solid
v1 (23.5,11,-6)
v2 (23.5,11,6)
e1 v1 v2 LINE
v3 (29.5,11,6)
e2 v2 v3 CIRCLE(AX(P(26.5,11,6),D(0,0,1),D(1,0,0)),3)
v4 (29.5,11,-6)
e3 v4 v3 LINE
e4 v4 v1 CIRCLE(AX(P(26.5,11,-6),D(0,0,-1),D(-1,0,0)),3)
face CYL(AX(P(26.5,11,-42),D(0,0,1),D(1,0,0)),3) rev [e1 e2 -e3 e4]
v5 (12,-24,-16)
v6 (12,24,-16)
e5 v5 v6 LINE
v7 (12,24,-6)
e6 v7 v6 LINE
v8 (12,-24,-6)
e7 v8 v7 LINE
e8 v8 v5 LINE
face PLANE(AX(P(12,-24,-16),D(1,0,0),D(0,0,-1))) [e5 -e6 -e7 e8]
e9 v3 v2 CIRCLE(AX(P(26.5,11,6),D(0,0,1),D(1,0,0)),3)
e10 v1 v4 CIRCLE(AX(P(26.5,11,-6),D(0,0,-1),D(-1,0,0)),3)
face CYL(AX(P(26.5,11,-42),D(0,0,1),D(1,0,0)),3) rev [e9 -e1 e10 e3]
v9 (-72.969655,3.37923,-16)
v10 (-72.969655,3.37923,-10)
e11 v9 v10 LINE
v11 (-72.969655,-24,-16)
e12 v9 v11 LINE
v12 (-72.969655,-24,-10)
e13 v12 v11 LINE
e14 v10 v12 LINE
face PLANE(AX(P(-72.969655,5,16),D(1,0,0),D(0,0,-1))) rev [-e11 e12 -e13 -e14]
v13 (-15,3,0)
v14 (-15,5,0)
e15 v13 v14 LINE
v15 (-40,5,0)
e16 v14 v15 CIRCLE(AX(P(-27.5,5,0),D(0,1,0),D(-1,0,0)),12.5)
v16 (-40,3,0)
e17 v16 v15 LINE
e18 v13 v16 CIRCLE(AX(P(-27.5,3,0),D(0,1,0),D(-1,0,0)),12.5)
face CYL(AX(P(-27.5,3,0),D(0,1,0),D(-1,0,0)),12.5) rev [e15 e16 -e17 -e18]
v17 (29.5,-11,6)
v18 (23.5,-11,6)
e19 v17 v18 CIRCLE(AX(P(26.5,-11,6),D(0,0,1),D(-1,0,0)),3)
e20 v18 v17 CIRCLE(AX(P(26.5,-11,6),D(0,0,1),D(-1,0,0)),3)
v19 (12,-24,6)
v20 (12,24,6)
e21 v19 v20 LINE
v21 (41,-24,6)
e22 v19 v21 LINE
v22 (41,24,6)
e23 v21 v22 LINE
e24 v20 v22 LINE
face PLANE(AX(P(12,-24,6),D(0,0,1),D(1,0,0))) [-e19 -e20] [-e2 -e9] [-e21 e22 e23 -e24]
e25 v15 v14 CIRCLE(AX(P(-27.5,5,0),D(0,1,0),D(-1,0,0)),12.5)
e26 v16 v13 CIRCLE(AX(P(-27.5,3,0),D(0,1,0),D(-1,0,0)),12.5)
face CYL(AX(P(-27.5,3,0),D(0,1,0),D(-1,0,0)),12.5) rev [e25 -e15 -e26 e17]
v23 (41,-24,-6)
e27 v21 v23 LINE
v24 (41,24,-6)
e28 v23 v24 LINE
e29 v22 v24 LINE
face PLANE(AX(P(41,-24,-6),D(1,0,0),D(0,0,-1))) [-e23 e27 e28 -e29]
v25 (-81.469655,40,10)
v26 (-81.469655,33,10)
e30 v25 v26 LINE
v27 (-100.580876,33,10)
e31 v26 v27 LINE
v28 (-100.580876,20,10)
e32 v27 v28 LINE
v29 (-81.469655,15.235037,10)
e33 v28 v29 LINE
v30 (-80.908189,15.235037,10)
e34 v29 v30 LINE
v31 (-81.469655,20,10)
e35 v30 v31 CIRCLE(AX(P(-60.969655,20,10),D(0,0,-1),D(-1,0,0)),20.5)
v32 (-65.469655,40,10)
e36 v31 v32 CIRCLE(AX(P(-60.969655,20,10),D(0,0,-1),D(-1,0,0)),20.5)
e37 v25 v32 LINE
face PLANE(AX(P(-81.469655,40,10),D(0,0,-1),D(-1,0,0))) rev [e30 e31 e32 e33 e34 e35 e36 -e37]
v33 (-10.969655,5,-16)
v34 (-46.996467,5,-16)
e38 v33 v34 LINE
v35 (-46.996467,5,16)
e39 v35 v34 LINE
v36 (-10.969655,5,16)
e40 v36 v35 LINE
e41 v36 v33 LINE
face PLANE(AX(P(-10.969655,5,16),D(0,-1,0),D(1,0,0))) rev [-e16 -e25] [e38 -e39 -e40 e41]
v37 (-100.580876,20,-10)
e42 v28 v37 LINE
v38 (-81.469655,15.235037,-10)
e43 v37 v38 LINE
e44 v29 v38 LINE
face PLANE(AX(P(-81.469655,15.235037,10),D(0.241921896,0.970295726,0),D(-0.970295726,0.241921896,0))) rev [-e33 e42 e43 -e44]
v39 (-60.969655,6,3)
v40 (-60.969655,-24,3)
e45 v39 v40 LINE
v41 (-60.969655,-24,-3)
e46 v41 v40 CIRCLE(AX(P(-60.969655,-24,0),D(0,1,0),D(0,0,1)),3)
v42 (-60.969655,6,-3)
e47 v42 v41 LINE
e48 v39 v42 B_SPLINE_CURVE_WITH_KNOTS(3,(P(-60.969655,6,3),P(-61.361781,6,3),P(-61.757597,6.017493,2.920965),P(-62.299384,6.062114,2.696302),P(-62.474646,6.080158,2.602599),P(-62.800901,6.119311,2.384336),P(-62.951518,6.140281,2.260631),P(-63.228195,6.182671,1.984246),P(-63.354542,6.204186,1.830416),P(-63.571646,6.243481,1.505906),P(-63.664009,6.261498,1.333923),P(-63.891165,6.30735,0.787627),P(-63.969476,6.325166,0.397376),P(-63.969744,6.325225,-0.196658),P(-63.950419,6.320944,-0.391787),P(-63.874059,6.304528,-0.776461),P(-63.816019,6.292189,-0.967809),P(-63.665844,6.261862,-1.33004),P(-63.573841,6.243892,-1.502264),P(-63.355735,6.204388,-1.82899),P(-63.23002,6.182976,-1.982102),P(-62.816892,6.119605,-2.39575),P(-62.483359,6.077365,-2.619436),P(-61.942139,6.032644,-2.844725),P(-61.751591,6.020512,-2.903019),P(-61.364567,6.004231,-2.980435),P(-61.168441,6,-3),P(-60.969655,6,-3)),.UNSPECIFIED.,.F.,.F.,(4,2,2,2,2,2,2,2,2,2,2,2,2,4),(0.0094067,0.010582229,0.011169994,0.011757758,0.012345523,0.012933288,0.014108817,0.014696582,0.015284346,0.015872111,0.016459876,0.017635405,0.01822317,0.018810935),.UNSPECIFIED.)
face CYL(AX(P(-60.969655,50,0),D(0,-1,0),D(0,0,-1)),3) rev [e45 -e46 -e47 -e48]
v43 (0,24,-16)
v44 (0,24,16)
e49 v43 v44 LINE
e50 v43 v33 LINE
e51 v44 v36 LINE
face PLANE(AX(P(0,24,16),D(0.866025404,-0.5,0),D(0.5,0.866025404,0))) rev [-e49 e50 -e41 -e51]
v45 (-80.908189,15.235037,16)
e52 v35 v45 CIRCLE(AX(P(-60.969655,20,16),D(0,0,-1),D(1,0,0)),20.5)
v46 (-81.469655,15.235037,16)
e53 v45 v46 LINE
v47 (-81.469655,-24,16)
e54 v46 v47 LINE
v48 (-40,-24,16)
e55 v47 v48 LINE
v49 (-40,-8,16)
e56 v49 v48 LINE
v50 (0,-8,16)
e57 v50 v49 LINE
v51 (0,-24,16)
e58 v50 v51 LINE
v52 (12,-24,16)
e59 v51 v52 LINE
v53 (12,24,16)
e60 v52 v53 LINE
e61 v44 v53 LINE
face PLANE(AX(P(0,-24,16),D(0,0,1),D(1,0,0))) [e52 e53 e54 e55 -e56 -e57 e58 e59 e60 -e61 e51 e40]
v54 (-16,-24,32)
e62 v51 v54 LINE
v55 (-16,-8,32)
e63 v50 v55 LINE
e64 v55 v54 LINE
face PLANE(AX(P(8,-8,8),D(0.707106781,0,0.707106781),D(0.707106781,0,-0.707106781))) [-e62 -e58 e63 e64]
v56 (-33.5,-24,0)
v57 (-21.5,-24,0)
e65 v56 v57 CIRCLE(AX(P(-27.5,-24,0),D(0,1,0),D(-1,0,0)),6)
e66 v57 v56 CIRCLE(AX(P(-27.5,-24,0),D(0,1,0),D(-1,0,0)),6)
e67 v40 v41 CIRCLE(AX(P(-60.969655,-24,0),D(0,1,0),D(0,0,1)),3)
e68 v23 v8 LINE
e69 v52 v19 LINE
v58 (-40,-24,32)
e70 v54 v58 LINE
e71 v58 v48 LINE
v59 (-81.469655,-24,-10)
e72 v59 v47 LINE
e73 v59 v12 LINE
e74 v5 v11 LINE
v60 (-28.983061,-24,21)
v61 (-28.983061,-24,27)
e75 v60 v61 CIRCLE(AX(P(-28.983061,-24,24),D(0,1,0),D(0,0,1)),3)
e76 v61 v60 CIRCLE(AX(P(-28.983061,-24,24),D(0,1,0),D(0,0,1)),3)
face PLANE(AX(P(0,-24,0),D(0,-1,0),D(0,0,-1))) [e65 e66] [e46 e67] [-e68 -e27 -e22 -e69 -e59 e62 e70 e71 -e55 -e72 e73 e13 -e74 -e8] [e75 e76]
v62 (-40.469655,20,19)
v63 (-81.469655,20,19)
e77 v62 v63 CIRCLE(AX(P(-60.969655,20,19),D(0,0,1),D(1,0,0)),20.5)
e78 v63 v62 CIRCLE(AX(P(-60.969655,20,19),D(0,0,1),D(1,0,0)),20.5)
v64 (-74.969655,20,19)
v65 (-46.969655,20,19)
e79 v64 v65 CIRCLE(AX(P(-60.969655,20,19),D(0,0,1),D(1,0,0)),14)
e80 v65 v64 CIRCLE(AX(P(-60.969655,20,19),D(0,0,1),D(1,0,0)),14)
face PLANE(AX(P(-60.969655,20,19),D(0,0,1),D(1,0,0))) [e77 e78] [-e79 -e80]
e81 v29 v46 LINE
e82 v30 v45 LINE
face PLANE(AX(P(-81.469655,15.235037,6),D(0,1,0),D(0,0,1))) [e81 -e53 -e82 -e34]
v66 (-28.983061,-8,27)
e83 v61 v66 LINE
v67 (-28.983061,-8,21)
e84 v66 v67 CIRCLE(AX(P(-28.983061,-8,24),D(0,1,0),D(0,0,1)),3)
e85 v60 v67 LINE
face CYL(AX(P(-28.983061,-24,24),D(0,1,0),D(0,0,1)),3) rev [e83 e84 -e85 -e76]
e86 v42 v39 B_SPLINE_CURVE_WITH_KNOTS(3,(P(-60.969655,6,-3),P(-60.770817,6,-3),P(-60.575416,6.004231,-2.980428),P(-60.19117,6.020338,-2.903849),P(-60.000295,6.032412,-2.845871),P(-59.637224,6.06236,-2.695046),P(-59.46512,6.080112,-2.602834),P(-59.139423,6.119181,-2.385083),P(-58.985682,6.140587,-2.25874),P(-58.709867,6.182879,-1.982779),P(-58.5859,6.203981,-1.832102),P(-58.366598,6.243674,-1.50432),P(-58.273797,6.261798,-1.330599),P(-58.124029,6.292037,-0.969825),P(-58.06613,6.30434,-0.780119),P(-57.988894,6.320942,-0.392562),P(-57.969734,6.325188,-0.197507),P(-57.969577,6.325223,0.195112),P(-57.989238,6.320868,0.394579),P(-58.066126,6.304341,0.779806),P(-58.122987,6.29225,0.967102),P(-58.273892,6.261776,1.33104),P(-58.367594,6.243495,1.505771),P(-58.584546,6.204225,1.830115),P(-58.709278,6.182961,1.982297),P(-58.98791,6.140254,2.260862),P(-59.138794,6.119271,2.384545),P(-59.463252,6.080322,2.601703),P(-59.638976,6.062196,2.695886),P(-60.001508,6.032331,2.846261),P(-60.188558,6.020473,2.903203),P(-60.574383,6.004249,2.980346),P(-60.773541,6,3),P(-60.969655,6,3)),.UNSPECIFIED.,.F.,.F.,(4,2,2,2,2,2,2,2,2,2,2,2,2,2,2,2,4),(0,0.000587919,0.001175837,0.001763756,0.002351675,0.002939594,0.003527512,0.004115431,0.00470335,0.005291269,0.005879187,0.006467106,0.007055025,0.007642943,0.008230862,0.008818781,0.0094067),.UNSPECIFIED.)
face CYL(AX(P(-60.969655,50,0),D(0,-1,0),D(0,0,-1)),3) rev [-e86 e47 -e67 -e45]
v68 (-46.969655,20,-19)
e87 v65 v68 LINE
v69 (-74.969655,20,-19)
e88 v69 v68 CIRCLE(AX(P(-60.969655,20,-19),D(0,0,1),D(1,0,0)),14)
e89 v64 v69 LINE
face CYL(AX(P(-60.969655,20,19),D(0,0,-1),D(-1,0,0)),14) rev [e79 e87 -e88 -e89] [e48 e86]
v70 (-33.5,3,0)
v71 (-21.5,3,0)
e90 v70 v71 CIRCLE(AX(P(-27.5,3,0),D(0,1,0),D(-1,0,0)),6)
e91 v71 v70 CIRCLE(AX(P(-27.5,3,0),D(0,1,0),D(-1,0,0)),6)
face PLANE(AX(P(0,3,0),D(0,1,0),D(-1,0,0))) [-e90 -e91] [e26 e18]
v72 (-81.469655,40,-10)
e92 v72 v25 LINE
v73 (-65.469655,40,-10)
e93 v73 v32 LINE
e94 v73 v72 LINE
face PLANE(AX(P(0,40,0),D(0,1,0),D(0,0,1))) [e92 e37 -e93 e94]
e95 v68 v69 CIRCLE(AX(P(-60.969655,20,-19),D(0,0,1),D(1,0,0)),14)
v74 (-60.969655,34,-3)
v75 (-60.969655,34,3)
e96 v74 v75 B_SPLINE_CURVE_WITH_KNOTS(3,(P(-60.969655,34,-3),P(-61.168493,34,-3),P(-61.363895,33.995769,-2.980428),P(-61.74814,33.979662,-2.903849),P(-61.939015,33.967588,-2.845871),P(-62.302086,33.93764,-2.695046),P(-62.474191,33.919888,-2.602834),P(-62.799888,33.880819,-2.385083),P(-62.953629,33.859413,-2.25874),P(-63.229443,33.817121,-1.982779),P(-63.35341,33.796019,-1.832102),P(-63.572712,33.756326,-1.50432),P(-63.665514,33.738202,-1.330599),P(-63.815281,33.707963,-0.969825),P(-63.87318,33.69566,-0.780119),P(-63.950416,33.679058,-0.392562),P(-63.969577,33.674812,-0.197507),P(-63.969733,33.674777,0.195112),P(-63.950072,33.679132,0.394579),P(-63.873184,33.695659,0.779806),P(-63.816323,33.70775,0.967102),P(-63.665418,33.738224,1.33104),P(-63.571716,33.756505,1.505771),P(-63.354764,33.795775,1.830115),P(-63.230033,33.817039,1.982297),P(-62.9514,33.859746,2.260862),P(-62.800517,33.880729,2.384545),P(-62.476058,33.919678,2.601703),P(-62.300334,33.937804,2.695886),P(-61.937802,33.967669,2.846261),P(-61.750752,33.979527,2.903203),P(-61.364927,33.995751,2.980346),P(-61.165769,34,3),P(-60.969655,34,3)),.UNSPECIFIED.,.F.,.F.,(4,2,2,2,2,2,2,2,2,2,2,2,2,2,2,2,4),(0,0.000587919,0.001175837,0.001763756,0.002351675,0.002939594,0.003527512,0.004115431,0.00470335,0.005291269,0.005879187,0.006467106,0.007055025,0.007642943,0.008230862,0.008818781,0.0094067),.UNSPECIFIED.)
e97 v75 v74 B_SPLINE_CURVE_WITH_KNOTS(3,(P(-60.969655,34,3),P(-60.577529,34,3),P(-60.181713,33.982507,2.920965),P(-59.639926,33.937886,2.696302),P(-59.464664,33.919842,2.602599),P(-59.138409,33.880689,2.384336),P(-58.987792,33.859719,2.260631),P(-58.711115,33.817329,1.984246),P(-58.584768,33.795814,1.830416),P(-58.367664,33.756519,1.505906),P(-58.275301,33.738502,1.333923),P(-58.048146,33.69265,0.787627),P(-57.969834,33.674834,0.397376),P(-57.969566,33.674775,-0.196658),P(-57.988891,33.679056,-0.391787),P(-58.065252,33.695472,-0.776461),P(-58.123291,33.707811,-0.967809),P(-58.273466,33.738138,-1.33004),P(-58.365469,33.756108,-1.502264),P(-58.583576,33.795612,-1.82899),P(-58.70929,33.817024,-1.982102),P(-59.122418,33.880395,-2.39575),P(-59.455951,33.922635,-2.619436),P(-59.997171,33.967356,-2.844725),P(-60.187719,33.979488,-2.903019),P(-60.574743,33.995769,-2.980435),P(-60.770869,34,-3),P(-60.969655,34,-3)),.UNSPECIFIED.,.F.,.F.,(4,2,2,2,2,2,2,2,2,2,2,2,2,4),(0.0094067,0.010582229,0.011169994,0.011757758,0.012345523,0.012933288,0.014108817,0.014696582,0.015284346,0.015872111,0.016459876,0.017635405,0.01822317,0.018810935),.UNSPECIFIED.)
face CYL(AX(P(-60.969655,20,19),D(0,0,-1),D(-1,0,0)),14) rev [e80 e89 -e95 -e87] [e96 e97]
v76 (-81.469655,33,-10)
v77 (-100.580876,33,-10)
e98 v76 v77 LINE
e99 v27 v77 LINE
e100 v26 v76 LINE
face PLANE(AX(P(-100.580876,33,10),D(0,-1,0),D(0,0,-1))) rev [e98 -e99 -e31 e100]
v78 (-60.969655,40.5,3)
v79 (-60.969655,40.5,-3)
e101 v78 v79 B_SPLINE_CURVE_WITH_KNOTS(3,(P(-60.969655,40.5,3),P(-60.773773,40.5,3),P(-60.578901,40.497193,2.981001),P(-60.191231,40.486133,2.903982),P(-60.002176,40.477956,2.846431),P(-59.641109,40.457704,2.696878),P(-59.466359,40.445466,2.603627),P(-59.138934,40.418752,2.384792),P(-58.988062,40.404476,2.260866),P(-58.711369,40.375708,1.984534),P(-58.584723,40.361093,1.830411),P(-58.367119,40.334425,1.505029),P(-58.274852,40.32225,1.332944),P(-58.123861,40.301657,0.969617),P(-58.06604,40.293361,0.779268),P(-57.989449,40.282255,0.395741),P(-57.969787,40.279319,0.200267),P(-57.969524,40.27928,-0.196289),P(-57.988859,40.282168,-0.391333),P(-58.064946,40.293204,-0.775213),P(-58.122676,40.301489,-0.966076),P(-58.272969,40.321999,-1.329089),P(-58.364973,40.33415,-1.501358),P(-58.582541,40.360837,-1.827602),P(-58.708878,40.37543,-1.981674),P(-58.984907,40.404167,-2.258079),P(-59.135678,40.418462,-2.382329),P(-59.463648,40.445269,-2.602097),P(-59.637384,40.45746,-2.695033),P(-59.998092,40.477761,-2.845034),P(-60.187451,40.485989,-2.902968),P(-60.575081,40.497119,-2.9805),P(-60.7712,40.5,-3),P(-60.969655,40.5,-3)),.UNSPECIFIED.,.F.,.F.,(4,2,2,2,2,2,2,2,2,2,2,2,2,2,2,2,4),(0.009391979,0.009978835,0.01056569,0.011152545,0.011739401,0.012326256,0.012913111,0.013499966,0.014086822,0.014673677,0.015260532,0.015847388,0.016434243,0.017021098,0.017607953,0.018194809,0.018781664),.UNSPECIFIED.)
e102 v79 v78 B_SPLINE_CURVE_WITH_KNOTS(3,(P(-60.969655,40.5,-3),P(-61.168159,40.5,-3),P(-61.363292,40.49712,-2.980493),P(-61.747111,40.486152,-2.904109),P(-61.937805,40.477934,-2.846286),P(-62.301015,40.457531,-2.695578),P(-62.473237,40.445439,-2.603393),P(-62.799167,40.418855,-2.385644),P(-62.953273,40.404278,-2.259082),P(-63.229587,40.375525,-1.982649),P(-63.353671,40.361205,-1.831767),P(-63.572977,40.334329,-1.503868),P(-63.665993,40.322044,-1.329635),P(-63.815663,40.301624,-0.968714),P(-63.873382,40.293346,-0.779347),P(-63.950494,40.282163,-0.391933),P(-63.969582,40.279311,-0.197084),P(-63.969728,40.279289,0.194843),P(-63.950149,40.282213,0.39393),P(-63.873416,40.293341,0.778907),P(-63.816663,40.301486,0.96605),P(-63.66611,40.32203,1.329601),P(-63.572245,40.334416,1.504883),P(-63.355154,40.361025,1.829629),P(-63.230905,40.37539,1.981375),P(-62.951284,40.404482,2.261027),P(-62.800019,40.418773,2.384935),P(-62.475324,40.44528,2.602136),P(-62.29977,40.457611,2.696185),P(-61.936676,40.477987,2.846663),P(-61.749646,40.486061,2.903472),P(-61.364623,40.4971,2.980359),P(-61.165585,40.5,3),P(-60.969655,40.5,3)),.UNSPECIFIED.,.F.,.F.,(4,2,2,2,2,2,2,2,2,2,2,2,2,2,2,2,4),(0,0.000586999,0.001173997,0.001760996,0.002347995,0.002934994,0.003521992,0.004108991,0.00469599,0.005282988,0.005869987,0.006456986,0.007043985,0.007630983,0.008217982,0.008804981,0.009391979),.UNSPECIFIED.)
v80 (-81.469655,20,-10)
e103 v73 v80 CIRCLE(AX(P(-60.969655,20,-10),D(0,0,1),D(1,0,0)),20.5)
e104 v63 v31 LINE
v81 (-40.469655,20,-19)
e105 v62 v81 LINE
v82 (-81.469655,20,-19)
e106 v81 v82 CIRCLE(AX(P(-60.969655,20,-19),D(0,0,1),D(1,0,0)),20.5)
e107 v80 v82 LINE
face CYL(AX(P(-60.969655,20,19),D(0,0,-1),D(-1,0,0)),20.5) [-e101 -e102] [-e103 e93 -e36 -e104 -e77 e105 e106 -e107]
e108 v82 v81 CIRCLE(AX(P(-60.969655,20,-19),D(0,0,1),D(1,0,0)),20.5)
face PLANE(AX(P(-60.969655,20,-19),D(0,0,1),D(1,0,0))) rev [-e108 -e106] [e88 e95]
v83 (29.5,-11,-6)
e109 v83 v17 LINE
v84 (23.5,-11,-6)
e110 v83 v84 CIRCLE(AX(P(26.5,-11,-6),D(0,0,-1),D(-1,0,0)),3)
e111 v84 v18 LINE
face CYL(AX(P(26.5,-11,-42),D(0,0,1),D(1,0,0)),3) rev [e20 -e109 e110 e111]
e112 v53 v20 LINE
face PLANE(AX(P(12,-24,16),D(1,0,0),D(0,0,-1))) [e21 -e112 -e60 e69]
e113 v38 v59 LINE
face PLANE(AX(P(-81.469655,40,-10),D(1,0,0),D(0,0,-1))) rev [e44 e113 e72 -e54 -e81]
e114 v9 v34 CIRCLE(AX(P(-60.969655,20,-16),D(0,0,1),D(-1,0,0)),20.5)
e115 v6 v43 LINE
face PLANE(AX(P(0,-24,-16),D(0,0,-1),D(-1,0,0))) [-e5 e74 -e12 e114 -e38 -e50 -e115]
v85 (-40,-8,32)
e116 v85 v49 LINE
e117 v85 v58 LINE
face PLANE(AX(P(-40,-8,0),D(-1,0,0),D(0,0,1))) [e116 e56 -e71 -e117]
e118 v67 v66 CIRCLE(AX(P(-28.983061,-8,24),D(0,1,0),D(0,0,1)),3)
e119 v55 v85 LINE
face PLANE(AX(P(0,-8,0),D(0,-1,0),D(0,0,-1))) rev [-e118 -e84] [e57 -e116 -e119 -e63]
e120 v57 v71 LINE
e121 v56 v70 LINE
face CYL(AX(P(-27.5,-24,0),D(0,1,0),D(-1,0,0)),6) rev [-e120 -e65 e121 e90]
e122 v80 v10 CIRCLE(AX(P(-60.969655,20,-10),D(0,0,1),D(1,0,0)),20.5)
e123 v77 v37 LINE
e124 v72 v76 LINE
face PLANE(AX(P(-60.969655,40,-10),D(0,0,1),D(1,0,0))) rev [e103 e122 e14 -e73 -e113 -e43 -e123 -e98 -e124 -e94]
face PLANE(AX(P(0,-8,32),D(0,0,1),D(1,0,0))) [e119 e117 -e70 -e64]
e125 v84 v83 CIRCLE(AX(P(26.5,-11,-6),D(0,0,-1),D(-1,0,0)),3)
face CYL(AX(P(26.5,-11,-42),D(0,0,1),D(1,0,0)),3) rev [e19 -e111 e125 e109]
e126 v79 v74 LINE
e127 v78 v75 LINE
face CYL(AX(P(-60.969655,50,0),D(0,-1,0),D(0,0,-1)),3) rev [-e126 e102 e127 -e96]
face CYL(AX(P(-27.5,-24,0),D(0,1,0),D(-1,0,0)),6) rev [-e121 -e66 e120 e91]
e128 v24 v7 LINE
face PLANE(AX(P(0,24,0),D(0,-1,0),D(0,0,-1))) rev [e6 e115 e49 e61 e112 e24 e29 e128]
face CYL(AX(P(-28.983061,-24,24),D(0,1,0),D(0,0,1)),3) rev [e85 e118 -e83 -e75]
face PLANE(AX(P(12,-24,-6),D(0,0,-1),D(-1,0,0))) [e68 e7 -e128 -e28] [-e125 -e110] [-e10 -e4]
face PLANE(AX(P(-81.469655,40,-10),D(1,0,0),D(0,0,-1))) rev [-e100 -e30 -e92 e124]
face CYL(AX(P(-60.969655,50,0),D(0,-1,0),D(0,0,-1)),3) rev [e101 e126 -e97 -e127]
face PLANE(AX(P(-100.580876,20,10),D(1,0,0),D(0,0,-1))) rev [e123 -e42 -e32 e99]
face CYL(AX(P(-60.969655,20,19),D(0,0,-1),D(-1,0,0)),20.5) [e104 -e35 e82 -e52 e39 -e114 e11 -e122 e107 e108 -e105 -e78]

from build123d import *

# Parameters (mm, degrees)
BASE_BLOCK_DEPTH           = 24
BASE_SLOT_SKETCH_R         = 3
BASE_SLOT_22X6_DEPTH       = 48
ANGLED_WEB_DEPTH           = 16
UPPER_BLOCK_SKETCH_R       = 20.5
UPPER_BLOCK_SKETCH_R_2     = 14
UPPER_BLOCK_DEPTH          = 19
SIDE_LUG_SKETCH_W          = 24
SIDE_LUG_SKETCH_H          = 16
SIDE_LUG_DEPTH             = 16
LUG_HOLE_SKETCH_R          = 3
LUG_HOLE_6_DEPTH           = 16
SPOT_FACE_RECESS_SKETCH_R  = 12.5
SPOT_FACE_RECESS_2MM_DEPTH = 2
SPOT_FACE_HOLE_SKETCH_R    = 6
SPOT_FACE_HOLE_12_DEPTH    = 96.223708731
VERTICAL_BORE_SKETCH_R     = 3
VERTICAL_BORE_CUT_DEPTH    = 50
PIVOT_HOUSING_DEPTH        = 40
TOP_PIN_HOLE_DEPTH         = 97.444568168
TOP_PIN_HOLE_DEPTH_BACK    = 97.444568168
TOP_PIN_HOLE_SKETCH_R      = 3
FRONT_PIN_HOLE_DEPTH       = 97.444568168
FRONT_PIN_HOLE_DEPTH_BACK  = 97.444568168
FRONT_PIN_HOLE_SKETCH_R    = 14
REAR_PAD_SKETCH_W          = 8.5
REAR_PAD_SKETCH_H          = 24
REAR_PAD_DEPTH             = 20
ANGLED_PAD_DEPTH           = 10
CONNECTING_RIB_DEPTH       = 10


with BuildPart() as part:
    # Base Block Sketch → Base Block (new, symmetric)
    with BuildSketch(Plane(origin=(0, 0, 0), x_dir=(1, 0, 0), z_dir=(0, 1, 0))):
        Polygon((0, -16), (0, 16), (12, 16), (12, 6), (41, 6), (41, -6), (12, -6), (12, -16), align=None)
    extrude(amount=BASE_BLOCK_DEPTH, both=True)

    # Base Slot Sketch → Base Slot 22x6 (cut)
    with BuildSketch(Plane.XY.offset(6)):
        with Locations((26.5, 11)):
            Circle(BASE_SLOT_SKETCH_R)
        with Locations(Location((26.5, -11, 0), (0, 0, 180))):
            Circle(BASE_SLOT_SKETCH_R)
    extrude(amount=-BASE_SLOT_22X6_DEPTH, mode=Mode.SUBTRACT)

    # Angled Web Sketch → Angled Web (add, symmetric)
    with BuildSketch(Plane.XY):
        Polygon((0, -24), (0, 24), (-10.969655115, 5), (-72.969655115, 5), (-72.969655115, -24), align=None)
    extrude(amount=ANGLED_WEB_DEPTH, both=True)

    # Upper Block Sketch → Upper Block (add, symmetric)
    with BuildSketch(Plane.XY):
        with Locations((-60.969655115, 20)):
            Circle(UPPER_BLOCK_SKETCH_R)
        with Locations((-60.969655115, 20)):
            Circle(UPPER_BLOCK_SKETCH_R_2, mode=Mode.SUBTRACT)
    extrude(amount=UPPER_BLOCK_DEPTH, both=True)

    # Side Lug Sketch → Side Lug (add)
    with BuildSketch(Plane.XZ.offset(24)):
        with Locations((-28, 24)):
            Rectangle(SIDE_LUG_SKETCH_W, SIDE_LUG_SKETCH_H)
        Polygon((-16, 16), (0, 16), (-16, 32), align=None)
    extrude(amount=-SIDE_LUG_DEPTH)

    # Lug Hole Sketch → Lug Hole Ø6 (cut)
    with BuildSketch(Plane(origin=(0, -8, 0), x_dir=(1, 0, 0), z_dir=(0, 1, 0))):
        with Locations(Location((-28.983060808, -24, 0), (0, 0, 270))):
            Circle(LUG_HOLE_SKETCH_R)
    extrude(amount=-LUG_HOLE_6_DEPTH, mode=Mode.SUBTRACT)

    # Spot Face Recess Sketch → Spot Face Recess 2mm (cut)
    with BuildSketch(Plane(origin=(0, 5, 0), x_dir=(1, 0, 0), z_dir=(0, 1, 0))):
        with Locations(Location((-27.5, 0, 0), (0, 0, 180))):
            Circle(SPOT_FACE_RECESS_SKETCH_R)
    extrude(amount=-SPOT_FACE_RECESS_2MM_DEPTH, mode=Mode.SUBTRACT)

    # Spot Face Hole Sketch → Spot Face Hole Ø12 (cut, through all)
    with BuildSketch(Plane(origin=(0, 3, 0), x_dir=(1, 0, 0), z_dir=(0, 1, 0))):
        with Locations(Location((-27.5, 0, 0), (0, 0, 180))):
            Circle(SPOT_FACE_HOLE_SKETCH_R)
    extrude(amount=-SPOT_FACE_HOLE_12_DEPTH, mode=Mode.SUBTRACT)

    # Vertical Bore Sketch → Vertical Bore Cut (cut)
    with BuildSketch(Plane(origin=(0, 0, 0), x_dir=(1, 0, 0), z_dir=(0, 1, 0))):
        with Locations(Location((-60.969655115, 0, 0), (0, 0, 90))):
            Circle(VERTICAL_BORE_SKETCH_R)
    extrude(amount=VERTICAL_BORE_CUT_DEPTH, mode=Mode.SUBTRACT)

    # Pivot Housing Sketch → Pivot Housing (add)
    with BuildSketch(Plane(origin=(0, 0, 0), x_dir=(1, 0, 0), z_dir=(0, 1, 0))):
        Polygon((-60.969655115, 0), (-60.969655115, 10), (-81.469655115, 10), (-81.469655115, -10), (-60.969655115, -10), align=None)
    extrude(amount=PIVOT_HOUSING_DEPTH)

    # Top Pin Hole Sketch → Top Pin Hole (cut, two sides: drawn at the far end of the back side and taken through both)
    with BuildSketch(Plane(origin=(0, 0, 0), x_dir=(1, 0, 0), z_dir=(0, 1, 0)).offset(-TOP_PIN_HOLE_DEPTH_BACK)):
        with Locations(Location((-60.969655115, 0, 0), (0, 0, 90))):
            Circle(TOP_PIN_HOLE_SKETCH_R)
    extrude(amount=TOP_PIN_HOLE_DEPTH + TOP_PIN_HOLE_DEPTH_BACK, mode=Mode.SUBTRACT)

    # Front Pin Hole Sketch → Front Pin Hole (cut, two sides: drawn at the far end of the back side and taken through both)
    with BuildSketch(Plane.XY.offset(-FRONT_PIN_HOLE_DEPTH_BACK)):
        with Locations((-60.969655115, 20)):
            Circle(FRONT_PIN_HOLE_SKETCH_R)
    extrude(amount=FRONT_PIN_HOLE_DEPTH + FRONT_PIN_HOLE_DEPTH_BACK, mode=Mode.SUBTRACT)

    # Rear Pad Sketch → Rear Pad (add)
    with BuildSketch(Plane.XY.offset(10)):
        with Locations((-77.219655115, -12)):
            Rectangle(REAR_PAD_SKETCH_W, REAR_PAD_SKETCH_H)
    extrude(amount=-REAR_PAD_DEPTH)

    # Angled Pad Sketch → Angled Pad (add, symmetric)
    with BuildSketch(Plane.XY):
        Polygon((-100.580876389, 20), (-100.580876389, 33), (-81.469655115, 33), (-81.469655115, 15.235037368), align=None)
    extrude(amount=ANGLED_PAD_DEPTH, both=True)

    # Connecting Rib Sketch → Connecting Rib (add)
    with BuildSketch(Plane.XY.offset(16)):
        with BuildLine():
            Line((-72.969655115, -24), (-81.469655115, -24))
            Line((-81.469655115, -24), (-81.469655115, 15.235037368))
            Line((-81.469655115, 15.235037368), (-80.90818894, 15.235037368))
            ThreePointArc((-80.90818894, 15.235037368), (-78.003666053, 8.594191332), (-72.969655115, 3.379229861))
            Line((-72.969655115, 3.379229861), (-72.969655115, -24))
        make_face()
    extrude(amount=-CONNECTING_RIB_DEPTH)


solid = part.part
